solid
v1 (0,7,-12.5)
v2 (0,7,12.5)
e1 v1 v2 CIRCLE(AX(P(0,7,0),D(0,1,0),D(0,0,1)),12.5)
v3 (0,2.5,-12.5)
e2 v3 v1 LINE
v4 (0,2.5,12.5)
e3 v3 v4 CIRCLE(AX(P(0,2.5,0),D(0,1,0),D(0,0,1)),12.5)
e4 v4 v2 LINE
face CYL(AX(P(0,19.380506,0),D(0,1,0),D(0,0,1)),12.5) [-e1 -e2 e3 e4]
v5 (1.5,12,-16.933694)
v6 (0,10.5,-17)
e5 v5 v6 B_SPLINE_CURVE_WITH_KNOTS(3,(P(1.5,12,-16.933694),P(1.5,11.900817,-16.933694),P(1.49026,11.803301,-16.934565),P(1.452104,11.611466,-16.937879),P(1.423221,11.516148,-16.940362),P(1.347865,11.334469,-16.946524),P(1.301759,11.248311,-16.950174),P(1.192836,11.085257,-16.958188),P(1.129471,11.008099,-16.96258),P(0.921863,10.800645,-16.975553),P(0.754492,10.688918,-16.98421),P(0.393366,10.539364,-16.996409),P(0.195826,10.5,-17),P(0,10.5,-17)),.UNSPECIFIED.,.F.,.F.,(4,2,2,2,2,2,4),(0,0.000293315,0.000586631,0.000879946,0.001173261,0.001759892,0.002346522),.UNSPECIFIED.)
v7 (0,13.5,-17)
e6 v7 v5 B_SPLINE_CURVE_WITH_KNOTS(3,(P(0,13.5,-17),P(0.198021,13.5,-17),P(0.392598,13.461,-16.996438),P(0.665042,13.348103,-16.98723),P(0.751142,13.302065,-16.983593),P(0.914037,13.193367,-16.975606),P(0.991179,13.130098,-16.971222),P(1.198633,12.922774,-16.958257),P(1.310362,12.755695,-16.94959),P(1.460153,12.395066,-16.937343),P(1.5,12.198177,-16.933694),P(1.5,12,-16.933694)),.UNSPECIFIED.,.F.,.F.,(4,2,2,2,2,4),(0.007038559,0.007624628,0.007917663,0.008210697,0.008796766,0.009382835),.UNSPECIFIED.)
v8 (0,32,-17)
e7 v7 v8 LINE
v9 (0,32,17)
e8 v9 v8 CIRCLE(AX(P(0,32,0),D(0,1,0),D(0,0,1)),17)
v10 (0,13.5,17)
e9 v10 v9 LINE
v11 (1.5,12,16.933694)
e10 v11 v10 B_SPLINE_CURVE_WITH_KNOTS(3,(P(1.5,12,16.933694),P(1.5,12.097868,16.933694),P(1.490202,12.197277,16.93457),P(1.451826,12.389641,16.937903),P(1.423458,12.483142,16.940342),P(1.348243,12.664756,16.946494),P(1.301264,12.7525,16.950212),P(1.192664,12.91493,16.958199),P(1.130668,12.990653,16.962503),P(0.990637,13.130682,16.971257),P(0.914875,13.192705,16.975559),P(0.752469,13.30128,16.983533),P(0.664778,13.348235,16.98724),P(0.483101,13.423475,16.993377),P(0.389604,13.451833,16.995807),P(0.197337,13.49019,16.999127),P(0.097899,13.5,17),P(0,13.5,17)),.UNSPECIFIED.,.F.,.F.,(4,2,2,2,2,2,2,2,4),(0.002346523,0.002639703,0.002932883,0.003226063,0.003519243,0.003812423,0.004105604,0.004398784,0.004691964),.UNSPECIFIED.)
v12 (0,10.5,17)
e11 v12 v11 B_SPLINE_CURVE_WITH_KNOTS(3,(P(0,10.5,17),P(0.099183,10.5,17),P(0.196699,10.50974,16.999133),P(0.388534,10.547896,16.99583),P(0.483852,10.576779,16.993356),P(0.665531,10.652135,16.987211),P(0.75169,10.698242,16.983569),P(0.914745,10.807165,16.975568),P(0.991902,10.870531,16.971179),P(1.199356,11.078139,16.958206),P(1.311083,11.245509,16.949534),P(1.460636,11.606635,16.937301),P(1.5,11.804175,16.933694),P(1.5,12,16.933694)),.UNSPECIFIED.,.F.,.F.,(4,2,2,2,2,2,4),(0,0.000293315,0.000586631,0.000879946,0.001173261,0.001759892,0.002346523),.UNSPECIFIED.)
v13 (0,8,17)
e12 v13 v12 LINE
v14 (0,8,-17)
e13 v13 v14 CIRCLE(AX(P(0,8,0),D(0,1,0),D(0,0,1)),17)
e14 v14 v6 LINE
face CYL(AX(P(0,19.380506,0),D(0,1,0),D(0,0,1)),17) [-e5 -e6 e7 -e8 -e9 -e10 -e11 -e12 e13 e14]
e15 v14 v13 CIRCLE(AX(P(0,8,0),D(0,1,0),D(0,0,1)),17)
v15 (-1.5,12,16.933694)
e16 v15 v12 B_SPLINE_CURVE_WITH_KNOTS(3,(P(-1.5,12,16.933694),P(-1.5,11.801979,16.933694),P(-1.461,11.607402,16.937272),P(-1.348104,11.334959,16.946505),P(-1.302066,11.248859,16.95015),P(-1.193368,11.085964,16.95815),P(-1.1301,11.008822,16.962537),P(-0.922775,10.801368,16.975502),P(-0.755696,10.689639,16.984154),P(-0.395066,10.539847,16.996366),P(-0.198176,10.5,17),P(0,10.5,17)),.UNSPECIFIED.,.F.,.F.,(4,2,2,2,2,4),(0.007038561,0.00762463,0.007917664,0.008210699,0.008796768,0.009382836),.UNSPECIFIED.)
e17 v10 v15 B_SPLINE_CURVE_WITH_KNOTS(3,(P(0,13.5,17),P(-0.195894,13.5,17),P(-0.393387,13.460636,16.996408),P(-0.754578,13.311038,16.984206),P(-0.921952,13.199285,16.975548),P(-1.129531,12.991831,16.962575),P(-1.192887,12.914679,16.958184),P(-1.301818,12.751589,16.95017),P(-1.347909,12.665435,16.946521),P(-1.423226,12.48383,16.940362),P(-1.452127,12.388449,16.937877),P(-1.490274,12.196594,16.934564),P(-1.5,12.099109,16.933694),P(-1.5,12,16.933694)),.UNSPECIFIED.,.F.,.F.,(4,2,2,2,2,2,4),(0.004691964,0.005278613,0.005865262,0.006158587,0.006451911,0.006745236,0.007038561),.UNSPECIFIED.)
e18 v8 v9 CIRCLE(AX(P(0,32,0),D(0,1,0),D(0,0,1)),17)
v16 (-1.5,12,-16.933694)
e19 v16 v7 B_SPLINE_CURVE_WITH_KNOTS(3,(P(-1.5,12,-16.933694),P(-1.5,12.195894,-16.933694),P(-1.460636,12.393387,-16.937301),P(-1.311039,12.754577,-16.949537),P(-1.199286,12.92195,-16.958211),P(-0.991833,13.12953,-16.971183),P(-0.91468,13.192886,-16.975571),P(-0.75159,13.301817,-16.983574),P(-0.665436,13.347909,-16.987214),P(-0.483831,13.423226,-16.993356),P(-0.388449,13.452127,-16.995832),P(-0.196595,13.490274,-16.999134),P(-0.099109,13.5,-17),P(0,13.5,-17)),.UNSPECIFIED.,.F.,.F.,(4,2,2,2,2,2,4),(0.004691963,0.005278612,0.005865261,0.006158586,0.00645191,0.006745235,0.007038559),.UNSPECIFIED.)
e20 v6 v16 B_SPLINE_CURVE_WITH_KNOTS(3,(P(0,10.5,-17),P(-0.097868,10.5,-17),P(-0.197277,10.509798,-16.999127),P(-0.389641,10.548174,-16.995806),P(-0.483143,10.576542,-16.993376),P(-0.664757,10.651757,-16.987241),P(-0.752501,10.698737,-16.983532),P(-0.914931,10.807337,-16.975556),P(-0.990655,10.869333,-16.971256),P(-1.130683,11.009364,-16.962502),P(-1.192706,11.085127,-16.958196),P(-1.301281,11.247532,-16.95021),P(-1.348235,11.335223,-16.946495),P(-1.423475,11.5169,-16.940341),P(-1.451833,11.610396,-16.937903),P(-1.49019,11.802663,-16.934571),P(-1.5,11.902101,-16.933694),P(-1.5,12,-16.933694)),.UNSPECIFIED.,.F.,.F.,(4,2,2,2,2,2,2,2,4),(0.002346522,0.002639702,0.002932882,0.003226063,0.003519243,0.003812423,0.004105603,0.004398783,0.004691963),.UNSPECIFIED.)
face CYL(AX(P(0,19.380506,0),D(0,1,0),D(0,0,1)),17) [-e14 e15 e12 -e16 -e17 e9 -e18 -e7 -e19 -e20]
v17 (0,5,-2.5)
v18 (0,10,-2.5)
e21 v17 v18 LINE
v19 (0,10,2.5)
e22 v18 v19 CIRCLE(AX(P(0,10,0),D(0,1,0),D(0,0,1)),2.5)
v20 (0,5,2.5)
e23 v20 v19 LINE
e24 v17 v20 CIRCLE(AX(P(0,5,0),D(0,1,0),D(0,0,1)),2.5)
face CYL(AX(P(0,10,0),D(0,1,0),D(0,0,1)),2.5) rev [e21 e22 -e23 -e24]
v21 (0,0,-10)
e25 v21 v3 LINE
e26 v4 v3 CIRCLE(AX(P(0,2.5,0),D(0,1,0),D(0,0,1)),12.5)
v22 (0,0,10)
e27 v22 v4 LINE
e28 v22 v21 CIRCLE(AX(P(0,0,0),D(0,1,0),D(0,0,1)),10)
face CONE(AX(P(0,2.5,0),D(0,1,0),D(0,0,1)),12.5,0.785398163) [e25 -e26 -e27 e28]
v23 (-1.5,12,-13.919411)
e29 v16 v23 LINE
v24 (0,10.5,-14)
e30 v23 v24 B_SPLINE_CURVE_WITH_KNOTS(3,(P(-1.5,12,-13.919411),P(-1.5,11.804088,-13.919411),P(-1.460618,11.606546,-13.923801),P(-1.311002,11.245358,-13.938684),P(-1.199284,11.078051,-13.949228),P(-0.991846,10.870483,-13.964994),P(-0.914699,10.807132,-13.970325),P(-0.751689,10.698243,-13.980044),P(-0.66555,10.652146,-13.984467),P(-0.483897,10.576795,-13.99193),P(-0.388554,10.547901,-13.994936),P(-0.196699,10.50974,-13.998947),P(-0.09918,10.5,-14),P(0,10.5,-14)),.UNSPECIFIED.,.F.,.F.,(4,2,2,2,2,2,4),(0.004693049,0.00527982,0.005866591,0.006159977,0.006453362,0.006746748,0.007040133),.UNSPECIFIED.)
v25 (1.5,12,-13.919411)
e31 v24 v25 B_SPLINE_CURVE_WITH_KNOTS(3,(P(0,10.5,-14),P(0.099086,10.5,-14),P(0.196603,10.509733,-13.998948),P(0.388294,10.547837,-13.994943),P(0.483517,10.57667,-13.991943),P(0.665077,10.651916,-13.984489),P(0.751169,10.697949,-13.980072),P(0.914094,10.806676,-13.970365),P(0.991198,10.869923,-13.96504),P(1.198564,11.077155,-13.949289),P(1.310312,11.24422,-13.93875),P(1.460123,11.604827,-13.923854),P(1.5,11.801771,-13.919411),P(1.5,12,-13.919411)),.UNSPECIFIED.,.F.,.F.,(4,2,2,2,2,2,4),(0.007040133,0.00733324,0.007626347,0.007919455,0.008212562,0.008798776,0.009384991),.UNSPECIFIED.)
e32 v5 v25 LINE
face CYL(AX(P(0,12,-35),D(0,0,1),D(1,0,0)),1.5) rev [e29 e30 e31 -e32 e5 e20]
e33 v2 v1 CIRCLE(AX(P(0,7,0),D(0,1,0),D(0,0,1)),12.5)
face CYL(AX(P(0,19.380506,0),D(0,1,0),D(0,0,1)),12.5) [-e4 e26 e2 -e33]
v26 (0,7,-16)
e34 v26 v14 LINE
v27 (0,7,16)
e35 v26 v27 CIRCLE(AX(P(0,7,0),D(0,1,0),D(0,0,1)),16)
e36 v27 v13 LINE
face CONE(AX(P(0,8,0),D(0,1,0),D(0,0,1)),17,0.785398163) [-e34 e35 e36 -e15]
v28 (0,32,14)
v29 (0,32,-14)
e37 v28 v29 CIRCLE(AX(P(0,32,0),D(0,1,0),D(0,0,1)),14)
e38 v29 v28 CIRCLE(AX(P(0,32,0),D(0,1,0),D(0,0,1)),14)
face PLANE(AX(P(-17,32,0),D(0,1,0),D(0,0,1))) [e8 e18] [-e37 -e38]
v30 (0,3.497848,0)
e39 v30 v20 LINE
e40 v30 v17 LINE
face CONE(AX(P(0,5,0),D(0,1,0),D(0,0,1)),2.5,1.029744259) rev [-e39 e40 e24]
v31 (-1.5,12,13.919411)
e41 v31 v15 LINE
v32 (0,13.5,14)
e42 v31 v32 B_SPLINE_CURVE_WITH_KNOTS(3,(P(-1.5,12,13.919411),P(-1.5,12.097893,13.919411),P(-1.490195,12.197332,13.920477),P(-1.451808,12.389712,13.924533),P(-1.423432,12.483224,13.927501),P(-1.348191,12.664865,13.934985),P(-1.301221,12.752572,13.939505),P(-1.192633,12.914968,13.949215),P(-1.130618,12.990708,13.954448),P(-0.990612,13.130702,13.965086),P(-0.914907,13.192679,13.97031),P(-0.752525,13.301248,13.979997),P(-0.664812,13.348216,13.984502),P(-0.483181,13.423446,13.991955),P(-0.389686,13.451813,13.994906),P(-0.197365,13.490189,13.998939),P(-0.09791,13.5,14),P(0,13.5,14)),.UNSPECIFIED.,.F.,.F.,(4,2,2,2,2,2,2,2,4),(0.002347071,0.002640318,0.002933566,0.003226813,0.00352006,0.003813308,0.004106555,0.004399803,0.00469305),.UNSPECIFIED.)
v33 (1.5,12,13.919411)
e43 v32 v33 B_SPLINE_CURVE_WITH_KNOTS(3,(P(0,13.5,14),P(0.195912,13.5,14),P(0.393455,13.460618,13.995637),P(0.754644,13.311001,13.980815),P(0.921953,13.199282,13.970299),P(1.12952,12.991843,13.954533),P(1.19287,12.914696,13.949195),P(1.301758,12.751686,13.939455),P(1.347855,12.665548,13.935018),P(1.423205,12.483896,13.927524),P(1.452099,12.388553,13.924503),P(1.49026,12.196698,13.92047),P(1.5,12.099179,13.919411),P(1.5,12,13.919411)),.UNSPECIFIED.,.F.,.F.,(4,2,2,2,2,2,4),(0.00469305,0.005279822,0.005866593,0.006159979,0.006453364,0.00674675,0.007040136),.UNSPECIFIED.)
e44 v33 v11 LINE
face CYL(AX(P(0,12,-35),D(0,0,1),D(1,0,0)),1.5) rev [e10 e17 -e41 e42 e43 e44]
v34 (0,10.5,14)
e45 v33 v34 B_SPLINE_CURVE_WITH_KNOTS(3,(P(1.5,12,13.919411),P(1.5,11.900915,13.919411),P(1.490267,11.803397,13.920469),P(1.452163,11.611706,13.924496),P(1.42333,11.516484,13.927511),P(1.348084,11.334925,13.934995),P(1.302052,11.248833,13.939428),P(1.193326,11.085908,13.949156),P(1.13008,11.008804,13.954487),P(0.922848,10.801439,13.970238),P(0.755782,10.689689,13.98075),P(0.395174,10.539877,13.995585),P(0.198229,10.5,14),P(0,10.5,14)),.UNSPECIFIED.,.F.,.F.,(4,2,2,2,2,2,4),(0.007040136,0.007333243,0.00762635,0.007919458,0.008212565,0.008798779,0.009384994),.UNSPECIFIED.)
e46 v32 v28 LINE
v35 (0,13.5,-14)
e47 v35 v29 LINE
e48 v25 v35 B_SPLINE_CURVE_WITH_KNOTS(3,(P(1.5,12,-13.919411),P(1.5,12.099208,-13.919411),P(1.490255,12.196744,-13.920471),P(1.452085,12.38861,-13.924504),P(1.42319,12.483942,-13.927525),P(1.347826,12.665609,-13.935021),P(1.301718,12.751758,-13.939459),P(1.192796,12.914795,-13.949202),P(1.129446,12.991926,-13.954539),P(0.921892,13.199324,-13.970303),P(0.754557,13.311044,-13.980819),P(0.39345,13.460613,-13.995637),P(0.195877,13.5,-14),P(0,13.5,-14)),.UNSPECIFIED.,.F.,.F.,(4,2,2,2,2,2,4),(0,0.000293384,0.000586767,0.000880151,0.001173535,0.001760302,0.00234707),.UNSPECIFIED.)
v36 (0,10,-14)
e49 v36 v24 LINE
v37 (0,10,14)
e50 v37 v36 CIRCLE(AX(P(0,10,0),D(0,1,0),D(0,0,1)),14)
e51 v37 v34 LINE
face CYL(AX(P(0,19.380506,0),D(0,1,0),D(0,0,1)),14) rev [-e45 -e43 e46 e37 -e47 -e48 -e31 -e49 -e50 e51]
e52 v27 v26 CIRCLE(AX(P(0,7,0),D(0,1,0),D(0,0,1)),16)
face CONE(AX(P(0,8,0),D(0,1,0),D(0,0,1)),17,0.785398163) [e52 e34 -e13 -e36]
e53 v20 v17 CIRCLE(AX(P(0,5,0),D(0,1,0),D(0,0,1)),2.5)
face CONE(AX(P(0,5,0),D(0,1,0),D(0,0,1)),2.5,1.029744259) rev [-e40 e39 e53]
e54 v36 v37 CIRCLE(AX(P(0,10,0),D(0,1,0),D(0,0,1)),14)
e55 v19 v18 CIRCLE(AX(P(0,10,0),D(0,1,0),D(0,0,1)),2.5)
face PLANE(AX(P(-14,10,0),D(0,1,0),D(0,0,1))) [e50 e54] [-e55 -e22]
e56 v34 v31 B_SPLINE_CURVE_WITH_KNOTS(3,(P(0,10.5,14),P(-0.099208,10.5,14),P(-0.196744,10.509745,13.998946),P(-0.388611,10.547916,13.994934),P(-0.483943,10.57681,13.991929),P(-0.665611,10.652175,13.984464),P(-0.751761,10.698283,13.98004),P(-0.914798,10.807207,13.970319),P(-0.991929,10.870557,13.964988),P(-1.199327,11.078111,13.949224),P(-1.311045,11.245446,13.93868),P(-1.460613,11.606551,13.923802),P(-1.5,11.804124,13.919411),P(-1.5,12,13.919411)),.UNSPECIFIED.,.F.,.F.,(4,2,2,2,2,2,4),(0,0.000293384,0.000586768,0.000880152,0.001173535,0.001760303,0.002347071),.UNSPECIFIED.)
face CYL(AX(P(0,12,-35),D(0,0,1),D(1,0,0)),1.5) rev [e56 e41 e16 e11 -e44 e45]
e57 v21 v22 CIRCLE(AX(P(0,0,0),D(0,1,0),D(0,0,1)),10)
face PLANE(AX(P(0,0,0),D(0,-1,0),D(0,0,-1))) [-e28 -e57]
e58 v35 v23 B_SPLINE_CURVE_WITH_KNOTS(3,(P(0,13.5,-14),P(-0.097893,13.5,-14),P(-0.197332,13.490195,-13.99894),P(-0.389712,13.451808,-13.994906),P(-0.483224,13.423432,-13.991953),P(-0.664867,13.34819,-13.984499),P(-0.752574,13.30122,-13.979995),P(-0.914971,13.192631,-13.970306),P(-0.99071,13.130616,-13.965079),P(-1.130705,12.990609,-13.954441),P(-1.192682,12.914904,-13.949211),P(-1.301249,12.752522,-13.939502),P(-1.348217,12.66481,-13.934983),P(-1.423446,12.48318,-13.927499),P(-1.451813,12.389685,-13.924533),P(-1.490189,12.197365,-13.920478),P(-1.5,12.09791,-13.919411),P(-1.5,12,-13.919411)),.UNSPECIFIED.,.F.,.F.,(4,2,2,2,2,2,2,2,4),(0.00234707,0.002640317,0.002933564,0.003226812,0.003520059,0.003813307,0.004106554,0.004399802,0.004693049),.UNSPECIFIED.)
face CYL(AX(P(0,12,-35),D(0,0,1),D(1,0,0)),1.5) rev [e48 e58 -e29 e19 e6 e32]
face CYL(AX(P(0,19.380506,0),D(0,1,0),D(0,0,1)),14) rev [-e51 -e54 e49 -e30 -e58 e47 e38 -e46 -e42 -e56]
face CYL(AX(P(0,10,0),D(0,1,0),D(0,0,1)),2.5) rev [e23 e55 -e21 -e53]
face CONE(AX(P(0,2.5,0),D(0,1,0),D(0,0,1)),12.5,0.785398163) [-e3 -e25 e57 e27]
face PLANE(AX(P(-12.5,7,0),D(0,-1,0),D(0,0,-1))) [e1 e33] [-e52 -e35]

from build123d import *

# Parameters (mm, degrees)
M6_TAPPED_HOLE1_D     = 5
M6_TAPPED_HOLE1_DEPTH = 5
M6_TAPPED_HOLE1_TIP   = 1.502151548
SKETCH4_R             = 1.5
CUT_EXTRUDE1_DEPTH    = 35


with BuildPart() as part:
    # Sketch1 → Revolve1 (revolve)
    with BuildSketch(Plane.XY, mode=Mode.PRIVATE) as revolve1_sk:
        Polygon((0, 0), (-10, 0), (-12.5, 2.5), (-12.5, 7), (-16, 7), (-17, 8), (-17, 32), (-14, 32), (-14, 10), (0, 10), align=None)
    revolve(revolve1_sk.sketch.rotate(Axis((0, 19.380505724, 0), (0, -1, 0)), 270), axis=Axis((0, 19.380505724, 0), (0, -1, 0)))

    # M6 Tapped Hole1
    with Locations(Plane(origin=(0, 10, 0), x_dir=(1, 0, 0), z_dir=(0, 1, 0))):
        with Locations((0, 0)):
            Hole(M6_TAPPED_HOLE1_D / 2, depth=M6_TAPPED_HOLE1_DEPTH)
            with Locations((0, 0, -(M6_TAPPED_HOLE1_DEPTH + M6_TAPPED_HOLE1_TIP / 2))):  # 118° drill point
                Cone(0, M6_TAPPED_HOLE1_D / 2, M6_TAPPED_HOLE1_TIP, mode=Mode.SUBTRACT)

    # Sketch4 → Cut-Extrude1 (cut, symmetric)
    with BuildSketch(Plane.XY):
        with Locations((0, 12)):
            Circle(SKETCH4_R)
    extrude(amount=CUT_EXTRUDE1_DEPTH, both=True, mode=Mode.SUBTRACT)


solid = part.part
